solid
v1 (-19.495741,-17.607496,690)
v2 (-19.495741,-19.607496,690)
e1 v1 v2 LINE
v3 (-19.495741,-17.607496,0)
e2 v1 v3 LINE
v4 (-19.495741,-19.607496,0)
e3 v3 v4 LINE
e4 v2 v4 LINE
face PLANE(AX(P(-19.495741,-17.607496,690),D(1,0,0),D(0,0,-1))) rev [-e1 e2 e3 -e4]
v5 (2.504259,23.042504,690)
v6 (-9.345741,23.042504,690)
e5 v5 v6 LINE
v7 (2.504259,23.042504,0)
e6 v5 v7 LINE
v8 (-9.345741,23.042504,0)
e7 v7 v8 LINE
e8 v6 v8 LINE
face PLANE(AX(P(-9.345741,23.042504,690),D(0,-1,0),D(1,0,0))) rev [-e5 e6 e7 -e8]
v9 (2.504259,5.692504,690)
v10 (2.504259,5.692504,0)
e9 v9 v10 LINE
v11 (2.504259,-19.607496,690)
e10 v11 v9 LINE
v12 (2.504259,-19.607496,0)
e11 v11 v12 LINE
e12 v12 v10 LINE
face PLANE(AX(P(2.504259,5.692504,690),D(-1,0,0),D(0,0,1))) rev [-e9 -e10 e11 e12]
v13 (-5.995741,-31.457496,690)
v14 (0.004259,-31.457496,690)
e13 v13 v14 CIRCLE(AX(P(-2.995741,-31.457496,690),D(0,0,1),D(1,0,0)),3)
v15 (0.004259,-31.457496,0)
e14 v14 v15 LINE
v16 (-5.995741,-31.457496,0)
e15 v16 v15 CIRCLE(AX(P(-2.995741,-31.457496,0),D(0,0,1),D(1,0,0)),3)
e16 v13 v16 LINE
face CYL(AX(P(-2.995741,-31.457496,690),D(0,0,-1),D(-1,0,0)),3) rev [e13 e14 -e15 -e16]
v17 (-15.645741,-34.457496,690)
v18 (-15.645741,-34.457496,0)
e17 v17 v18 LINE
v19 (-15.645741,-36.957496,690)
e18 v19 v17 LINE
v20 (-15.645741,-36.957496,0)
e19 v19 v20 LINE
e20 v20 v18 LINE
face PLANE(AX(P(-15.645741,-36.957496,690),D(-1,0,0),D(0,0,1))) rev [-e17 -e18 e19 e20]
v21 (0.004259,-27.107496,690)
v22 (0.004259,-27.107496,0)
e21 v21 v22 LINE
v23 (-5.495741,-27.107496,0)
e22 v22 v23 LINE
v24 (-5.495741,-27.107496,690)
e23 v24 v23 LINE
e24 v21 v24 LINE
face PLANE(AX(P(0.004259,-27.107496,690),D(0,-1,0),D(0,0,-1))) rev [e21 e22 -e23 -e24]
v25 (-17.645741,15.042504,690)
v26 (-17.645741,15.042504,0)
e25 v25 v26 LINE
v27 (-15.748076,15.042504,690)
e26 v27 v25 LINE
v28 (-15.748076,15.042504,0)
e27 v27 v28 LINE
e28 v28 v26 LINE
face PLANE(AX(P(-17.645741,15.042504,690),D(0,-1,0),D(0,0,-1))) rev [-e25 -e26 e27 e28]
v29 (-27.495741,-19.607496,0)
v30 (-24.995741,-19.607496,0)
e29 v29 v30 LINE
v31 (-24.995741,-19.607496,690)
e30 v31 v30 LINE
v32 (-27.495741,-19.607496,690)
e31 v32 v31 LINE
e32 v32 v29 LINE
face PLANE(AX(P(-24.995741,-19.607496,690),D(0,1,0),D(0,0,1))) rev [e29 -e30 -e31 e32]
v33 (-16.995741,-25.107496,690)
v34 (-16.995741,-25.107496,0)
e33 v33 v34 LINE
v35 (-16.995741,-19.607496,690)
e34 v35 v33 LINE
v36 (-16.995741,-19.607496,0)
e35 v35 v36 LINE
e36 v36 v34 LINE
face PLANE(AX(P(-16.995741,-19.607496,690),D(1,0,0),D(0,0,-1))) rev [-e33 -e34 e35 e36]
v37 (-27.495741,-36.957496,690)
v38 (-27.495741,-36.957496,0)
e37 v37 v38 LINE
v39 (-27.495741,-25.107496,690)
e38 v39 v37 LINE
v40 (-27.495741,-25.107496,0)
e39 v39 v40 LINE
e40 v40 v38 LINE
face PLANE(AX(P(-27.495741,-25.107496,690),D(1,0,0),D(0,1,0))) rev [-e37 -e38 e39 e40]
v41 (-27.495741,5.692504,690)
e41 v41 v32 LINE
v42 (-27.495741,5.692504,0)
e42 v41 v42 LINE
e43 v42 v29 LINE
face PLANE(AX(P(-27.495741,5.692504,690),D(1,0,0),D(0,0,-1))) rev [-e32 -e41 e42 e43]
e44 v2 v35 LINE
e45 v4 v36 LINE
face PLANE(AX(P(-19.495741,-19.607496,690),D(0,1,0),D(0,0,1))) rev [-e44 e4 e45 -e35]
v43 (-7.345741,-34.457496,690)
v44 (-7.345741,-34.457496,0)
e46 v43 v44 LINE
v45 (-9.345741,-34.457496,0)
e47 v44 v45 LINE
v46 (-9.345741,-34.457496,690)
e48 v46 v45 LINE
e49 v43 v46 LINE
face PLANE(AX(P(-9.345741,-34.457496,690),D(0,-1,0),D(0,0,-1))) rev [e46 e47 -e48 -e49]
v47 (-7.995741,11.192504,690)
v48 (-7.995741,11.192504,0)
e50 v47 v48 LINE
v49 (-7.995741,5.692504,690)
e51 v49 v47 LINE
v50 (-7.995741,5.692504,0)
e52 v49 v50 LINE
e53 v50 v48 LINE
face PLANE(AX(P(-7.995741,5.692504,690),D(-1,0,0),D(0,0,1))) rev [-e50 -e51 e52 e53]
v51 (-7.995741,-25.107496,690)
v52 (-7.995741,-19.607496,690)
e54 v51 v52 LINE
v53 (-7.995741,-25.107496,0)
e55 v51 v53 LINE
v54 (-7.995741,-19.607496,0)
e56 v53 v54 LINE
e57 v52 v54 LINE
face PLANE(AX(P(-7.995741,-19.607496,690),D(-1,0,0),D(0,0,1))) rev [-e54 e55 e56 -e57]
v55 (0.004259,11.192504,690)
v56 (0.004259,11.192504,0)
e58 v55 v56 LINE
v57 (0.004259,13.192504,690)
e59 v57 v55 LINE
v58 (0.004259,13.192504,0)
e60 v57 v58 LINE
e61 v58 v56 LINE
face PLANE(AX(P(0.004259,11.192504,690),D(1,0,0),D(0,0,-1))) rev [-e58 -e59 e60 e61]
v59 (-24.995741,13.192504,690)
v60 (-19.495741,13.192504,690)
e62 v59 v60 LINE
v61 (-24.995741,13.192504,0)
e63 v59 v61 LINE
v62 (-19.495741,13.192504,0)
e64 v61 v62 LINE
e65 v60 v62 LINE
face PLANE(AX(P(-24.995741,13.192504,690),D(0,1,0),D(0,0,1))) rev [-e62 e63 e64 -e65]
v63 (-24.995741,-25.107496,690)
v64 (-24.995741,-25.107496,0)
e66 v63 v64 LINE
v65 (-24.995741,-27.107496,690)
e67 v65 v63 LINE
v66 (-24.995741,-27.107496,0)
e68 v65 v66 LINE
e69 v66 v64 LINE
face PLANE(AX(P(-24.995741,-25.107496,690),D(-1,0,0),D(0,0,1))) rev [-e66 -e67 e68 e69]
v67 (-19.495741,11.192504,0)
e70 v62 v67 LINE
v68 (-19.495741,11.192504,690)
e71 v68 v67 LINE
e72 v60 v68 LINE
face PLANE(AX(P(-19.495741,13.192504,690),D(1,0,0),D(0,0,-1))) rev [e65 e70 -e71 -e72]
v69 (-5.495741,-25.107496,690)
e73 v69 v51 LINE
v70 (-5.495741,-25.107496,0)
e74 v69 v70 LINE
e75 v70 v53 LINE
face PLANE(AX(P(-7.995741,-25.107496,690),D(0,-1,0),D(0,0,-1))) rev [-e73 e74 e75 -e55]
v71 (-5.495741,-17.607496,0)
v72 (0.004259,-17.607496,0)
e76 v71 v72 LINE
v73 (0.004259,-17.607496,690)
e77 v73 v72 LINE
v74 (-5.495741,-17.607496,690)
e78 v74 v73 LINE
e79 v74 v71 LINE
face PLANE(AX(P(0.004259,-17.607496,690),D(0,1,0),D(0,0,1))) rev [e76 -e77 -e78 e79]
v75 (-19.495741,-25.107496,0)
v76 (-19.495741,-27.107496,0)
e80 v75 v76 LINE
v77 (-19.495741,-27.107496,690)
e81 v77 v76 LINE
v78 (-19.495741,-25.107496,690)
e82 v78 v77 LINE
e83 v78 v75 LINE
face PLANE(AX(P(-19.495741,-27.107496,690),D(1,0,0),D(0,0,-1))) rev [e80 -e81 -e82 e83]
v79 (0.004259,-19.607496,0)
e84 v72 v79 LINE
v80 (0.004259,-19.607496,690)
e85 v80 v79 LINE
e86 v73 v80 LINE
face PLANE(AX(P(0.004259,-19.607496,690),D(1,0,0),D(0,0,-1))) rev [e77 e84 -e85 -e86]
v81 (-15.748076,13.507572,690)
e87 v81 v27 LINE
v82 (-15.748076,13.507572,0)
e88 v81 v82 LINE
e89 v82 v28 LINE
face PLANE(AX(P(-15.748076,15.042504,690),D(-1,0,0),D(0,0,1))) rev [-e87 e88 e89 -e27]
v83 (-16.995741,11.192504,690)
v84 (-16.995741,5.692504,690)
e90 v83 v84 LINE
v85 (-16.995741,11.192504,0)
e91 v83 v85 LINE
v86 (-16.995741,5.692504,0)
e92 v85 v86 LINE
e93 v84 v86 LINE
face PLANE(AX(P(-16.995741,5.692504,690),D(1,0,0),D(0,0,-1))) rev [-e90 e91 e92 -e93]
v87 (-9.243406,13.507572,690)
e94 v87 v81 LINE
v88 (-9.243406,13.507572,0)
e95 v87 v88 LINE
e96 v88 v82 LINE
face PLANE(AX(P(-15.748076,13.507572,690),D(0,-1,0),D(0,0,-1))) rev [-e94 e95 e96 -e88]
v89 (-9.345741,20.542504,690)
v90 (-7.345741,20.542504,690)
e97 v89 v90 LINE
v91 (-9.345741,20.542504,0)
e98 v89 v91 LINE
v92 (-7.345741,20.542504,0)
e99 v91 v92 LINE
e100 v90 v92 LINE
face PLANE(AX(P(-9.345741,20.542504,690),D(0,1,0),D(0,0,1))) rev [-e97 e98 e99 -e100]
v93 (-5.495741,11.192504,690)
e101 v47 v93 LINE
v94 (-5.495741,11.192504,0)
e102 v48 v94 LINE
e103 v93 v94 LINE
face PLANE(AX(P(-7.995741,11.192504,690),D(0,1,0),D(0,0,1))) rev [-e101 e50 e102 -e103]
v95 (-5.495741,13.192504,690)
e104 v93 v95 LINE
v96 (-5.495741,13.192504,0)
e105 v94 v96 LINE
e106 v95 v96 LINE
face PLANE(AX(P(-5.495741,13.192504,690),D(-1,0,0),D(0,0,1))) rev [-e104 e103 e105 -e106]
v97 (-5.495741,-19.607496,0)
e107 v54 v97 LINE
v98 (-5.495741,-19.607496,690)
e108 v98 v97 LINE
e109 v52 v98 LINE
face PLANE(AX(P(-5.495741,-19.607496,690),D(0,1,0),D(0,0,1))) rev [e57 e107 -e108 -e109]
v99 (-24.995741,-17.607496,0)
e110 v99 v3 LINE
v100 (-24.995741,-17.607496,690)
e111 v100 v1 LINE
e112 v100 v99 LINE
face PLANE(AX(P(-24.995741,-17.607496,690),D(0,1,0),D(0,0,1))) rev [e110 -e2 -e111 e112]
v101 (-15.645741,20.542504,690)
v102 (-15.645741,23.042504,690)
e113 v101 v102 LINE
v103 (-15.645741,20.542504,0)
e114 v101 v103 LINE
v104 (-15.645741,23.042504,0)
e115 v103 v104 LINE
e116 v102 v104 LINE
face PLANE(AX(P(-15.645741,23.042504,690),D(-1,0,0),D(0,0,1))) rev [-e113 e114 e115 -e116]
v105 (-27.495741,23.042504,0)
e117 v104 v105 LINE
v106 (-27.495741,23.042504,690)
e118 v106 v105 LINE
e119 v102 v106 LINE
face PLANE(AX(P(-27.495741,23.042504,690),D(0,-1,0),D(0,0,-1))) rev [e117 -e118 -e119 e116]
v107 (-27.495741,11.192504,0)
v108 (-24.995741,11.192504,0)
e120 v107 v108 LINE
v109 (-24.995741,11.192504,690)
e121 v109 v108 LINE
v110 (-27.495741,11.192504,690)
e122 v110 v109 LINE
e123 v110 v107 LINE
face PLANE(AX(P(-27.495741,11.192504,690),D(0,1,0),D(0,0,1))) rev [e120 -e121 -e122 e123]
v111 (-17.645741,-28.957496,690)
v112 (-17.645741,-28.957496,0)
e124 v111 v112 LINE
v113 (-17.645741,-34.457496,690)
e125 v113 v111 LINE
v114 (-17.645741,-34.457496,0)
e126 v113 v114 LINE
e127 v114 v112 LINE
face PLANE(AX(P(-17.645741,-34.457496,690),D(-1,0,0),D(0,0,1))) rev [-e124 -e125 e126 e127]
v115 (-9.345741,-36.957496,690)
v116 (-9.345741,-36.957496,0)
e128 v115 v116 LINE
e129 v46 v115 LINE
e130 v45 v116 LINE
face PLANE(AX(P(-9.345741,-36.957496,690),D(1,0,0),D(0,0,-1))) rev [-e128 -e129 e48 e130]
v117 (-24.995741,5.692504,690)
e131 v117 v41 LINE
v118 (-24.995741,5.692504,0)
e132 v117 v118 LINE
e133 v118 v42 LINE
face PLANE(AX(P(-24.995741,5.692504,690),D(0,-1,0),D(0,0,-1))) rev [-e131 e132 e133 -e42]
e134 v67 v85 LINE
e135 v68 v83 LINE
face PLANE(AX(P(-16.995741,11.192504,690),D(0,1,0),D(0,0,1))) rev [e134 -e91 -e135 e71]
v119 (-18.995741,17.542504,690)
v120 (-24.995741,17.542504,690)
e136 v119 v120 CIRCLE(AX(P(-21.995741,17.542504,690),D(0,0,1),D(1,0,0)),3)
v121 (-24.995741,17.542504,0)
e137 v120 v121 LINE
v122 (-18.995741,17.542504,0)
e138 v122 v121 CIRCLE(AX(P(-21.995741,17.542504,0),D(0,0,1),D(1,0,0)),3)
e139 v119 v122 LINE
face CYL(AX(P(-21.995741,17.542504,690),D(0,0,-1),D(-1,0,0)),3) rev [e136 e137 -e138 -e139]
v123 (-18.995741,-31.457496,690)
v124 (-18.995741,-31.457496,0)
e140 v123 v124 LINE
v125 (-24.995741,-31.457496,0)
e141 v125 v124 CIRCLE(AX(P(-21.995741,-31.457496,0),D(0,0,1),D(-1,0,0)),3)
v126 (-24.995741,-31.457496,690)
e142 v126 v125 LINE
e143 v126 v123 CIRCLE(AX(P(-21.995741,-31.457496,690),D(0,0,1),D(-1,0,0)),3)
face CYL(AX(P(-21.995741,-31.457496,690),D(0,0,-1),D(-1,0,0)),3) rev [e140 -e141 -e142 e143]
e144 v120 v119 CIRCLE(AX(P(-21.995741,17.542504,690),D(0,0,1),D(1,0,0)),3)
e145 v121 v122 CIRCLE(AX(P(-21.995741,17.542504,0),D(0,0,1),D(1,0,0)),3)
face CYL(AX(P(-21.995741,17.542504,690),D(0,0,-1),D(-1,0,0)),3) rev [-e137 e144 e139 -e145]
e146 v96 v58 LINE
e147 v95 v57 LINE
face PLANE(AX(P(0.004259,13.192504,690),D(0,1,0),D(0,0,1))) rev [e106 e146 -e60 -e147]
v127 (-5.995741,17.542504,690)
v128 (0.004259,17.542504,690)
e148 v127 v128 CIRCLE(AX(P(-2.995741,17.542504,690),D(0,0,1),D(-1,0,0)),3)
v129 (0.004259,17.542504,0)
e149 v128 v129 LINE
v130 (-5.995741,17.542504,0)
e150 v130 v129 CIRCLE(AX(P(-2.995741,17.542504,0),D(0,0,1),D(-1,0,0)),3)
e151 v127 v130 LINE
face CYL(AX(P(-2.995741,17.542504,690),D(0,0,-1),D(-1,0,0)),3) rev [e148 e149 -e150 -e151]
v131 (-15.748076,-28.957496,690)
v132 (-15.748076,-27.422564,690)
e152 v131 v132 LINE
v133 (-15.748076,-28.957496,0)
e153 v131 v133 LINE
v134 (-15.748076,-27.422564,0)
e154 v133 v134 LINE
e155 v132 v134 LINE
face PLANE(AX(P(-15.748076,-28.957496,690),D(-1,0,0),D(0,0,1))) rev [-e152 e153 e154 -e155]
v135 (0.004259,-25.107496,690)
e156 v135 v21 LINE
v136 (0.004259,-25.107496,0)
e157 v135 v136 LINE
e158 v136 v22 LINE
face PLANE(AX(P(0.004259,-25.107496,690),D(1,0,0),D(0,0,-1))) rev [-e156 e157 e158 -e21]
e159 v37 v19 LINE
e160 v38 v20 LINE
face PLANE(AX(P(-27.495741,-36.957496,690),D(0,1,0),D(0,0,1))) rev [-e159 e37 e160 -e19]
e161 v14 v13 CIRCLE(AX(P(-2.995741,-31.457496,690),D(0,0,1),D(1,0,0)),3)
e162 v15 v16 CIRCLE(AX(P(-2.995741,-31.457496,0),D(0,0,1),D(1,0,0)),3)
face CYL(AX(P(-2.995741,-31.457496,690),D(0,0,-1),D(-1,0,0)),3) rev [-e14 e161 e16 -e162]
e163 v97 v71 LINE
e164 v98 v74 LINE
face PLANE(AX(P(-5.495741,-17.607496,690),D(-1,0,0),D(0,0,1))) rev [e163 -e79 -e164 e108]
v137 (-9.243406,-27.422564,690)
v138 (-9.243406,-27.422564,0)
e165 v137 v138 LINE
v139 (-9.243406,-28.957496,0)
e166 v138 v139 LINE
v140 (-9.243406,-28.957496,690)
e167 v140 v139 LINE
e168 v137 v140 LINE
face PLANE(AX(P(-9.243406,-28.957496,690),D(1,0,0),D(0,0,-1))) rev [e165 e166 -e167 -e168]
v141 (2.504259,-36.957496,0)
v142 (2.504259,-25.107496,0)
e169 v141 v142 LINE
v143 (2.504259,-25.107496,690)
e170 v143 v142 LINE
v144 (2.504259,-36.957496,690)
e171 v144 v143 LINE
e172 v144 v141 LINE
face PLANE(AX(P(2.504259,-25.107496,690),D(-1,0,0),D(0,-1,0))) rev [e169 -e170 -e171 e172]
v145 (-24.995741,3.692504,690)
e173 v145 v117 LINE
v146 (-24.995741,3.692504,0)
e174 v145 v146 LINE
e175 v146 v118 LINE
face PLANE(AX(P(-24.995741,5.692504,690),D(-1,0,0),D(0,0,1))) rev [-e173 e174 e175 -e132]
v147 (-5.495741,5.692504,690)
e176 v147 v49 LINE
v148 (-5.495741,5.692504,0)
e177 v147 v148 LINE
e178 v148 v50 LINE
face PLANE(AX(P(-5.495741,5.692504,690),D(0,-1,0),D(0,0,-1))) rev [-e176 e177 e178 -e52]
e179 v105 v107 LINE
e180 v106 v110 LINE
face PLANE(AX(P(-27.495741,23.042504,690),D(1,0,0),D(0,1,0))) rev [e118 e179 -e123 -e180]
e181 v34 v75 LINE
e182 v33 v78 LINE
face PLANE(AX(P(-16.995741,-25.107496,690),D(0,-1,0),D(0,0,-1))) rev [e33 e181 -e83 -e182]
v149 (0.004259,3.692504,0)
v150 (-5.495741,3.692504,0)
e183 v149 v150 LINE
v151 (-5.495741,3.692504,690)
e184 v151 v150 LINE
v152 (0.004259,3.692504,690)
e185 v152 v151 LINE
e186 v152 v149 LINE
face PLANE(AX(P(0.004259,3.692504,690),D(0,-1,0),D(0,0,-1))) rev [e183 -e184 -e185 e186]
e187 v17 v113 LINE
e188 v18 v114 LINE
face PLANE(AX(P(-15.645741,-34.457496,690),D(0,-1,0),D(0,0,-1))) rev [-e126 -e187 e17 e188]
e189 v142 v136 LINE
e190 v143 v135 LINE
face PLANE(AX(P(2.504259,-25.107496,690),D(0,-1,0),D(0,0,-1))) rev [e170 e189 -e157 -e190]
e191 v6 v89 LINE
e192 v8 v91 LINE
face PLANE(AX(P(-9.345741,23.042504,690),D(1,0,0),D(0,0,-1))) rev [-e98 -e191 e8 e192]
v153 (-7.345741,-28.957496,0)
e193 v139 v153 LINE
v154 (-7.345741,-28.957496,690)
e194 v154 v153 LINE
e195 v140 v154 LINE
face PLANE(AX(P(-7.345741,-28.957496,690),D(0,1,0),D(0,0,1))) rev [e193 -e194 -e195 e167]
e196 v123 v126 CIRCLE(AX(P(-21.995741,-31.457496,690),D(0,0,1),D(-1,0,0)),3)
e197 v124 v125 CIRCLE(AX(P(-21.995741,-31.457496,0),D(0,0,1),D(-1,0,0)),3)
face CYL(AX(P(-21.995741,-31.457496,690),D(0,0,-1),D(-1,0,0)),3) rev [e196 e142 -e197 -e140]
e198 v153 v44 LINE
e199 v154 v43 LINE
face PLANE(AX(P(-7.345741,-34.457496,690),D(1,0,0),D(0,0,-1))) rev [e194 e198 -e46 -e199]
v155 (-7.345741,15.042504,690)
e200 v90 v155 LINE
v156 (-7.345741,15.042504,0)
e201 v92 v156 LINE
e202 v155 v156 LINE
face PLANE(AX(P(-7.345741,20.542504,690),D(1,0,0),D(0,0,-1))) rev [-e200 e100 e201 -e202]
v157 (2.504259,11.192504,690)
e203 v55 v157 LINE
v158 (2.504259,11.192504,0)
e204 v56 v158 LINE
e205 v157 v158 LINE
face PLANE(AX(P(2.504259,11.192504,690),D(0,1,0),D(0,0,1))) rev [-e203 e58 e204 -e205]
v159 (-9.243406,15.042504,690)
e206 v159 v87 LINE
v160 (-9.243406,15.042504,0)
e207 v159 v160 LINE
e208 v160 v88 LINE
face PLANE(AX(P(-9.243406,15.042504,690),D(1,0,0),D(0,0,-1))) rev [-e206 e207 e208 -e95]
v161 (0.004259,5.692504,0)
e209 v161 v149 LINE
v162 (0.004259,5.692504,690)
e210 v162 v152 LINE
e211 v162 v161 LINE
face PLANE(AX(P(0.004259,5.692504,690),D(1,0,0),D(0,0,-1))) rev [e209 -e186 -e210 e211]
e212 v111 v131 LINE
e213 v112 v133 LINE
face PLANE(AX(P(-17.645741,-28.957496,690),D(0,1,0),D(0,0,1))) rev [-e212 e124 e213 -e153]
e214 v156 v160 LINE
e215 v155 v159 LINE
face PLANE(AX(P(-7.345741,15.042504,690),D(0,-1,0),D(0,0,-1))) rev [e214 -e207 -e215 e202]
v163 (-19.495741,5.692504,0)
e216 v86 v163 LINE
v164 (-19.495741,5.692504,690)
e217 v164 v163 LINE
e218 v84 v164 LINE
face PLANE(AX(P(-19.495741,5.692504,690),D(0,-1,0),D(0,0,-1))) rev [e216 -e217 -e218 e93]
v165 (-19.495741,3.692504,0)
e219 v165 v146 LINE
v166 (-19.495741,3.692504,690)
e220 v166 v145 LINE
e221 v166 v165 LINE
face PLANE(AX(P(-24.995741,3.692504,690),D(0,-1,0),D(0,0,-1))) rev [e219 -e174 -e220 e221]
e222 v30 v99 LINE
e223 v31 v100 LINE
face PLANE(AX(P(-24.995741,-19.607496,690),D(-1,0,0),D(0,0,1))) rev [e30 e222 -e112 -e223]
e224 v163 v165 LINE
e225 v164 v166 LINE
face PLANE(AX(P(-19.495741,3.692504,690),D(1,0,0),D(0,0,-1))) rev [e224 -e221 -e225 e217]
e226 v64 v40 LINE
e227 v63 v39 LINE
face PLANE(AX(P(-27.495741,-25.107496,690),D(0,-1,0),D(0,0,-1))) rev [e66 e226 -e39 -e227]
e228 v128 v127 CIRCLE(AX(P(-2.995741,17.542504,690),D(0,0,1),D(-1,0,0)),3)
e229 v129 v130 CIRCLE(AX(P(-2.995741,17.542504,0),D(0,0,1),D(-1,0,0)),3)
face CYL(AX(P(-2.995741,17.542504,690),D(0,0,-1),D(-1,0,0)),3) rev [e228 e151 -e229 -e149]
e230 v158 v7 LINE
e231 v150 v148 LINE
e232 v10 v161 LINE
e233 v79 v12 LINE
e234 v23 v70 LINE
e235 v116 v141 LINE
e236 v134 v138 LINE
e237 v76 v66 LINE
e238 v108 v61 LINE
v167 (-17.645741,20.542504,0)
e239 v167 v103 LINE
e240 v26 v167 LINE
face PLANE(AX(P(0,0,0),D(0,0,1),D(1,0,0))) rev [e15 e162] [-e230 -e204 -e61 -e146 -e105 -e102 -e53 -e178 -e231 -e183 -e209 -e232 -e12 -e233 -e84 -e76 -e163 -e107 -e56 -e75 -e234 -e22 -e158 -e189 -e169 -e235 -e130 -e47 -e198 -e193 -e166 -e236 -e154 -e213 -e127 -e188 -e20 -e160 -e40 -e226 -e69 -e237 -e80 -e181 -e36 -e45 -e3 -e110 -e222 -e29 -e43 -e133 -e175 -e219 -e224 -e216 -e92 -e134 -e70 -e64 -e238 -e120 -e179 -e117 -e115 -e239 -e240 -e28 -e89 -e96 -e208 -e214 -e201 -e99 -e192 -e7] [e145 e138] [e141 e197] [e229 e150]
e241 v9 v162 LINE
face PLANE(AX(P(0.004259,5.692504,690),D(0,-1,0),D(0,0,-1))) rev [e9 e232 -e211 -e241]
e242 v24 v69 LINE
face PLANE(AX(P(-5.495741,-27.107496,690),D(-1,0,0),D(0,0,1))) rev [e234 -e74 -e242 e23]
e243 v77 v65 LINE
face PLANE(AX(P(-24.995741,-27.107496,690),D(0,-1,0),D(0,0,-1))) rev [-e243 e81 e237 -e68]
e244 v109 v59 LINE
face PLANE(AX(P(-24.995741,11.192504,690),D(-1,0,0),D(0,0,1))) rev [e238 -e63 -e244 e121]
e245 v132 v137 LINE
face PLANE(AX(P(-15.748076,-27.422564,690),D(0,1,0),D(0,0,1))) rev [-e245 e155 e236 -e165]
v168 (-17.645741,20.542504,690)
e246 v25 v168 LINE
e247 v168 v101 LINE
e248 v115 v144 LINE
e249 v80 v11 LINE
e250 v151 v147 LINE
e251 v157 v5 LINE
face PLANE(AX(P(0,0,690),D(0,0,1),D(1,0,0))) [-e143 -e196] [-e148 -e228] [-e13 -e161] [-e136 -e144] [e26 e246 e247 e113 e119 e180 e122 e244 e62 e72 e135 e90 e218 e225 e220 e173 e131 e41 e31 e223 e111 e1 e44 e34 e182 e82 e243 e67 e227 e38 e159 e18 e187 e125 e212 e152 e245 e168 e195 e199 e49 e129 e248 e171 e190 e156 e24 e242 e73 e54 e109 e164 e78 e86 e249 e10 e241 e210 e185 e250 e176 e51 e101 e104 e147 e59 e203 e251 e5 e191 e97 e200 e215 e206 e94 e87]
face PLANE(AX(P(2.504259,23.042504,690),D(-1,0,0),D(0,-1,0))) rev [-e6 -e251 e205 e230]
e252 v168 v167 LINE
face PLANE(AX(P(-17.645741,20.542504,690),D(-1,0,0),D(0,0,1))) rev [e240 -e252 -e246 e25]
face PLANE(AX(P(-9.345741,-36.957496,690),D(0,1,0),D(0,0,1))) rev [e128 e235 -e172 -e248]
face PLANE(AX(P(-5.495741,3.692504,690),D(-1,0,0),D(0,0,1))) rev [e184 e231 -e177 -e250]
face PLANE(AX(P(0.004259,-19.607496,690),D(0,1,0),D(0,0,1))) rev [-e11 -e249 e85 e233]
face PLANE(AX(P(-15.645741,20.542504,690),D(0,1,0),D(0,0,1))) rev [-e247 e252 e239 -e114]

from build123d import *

# Parameters (mm, degrees)
SKETCH_1_R      = 3
EXTRUDE_1_DEPTH = 690


with BuildPart() as part:
    # 草图1 → 凸台-拉伸1 (new body)
    with BuildSketch(Plane.XY):
        Polygon((-27.495741056, 11.192504259), (-24.995741056, 11.192504259), (-24.995741056, 13.192504259), (-19.495741056, 13.192504259), (-19.495741056, 11.192504259), (-16.995741056, 11.192504259), (-16.995741056, 5.692504259), (-19.495741056, 5.692504259), (-19.495741056, 3.692504259), (-24.995741056, 3.692504259), (-24.995741056, 5.692504259), (-27.495741056, 5.692504259), (-27.495741056, -19.607495741), (-24.995741056, -19.607495741), (-24.995741056, -17.607495741), (-19.495741056, -17.607495741), (-19.495741056, -19.607495741), (-16.995741056, -19.607495741), (-16.995741056, -25.107495741), (-19.495741056, -25.107495741), (-19.495741056, -27.107495741), (-24.995741056, -27.107495741), (-24.995741056, -25.107495741), (-27.495741056, -25.107495741), (-27.495741056, -36.957495741), (-15.645741056, -36.957495741), (-15.645741056, -34.457495741), (-17.645741056, -34.457495741), (-17.645741056, -28.957495741), (-15.748076247, -28.957495741), (-15.748076247, -27.422563567), (-9.243405866, -27.422563567), (-9.243405866, -28.957495741), (-7.345741056, -28.957495741), (-7.345741056, -34.457495741), (-9.345741056, -34.457495741), (-9.345741056, -36.957495741), (2.504258944, -36.957495741), (2.504258944, -25.107495741), (0.004258944, -25.107495741), (0.004258944, -27.107495741), (-5.495741056, -27.107495741), (-5.495741056, -25.107495741), (-7.995741056, -25.107495741), (-7.995741056, -19.607495741), (-5.495741056, -19.607495741), (-5.495741056, -17.607495741), (0.004258944, -17.607495741), (0.004258944, -19.607495741), (2.504258944, -19.607495741), (2.504258944, 5.692504259), (0.004258944, 5.692504259), (0.004258944, 3.692504259), (-5.495741056, 3.692504259), (-5.495741056, 5.692504259), (-7.995741056, 5.692504259), (-7.995741056, 11.192504259), (-5.495741056, 11.192504259), (-5.495741056, 13.192504259), (0.004258944, 13.192504259), (0.004258944, 11.192504259), (2.504258944, 11.192504259), (2.504258944, 23.042504259), (-9.345741056, 23.042504259), (-9.345741056, 20.542504259), (-7.345741056, 20.542504259), (-7.345741056, 15.042504259), (-9.243405866, 15.042504259), (-9.243405866, 13.507572085), (-15.748076247, 13.507572085), (-15.748076247, 15.042504259), (-17.645741056, 15.042504259), (-17.645741056, 20.542504259), (-15.645741056, 20.542504259), (-15.645741056, 23.042504259), (-27.495741056, 23.042504259), align=None)
        with Locations((-21.995741056, 17.542504259)):
            Circle(SKETCH_1_R, mode=Mode.SUBTRACT)
        with Locations(Location((-2.995741056, 17.542504259, 0), (0, 0, 180))):
            Circle(SKETCH_1_R, mode=Mode.SUBTRACT)
        with Locations((-2.995741056, -31.457495741)):
            Circle(SKETCH_1_R, mode=Mode.SUBTRACT)
        with Locations(Location((-21.995741056, -31.457495741, 0), (0, 0, 180))):
            Circle(SKETCH_1_R, mode=Mode.SUBTRACT)
    extrude(amount=EXTRUDE_1_DEPTH)


solid = part.part
